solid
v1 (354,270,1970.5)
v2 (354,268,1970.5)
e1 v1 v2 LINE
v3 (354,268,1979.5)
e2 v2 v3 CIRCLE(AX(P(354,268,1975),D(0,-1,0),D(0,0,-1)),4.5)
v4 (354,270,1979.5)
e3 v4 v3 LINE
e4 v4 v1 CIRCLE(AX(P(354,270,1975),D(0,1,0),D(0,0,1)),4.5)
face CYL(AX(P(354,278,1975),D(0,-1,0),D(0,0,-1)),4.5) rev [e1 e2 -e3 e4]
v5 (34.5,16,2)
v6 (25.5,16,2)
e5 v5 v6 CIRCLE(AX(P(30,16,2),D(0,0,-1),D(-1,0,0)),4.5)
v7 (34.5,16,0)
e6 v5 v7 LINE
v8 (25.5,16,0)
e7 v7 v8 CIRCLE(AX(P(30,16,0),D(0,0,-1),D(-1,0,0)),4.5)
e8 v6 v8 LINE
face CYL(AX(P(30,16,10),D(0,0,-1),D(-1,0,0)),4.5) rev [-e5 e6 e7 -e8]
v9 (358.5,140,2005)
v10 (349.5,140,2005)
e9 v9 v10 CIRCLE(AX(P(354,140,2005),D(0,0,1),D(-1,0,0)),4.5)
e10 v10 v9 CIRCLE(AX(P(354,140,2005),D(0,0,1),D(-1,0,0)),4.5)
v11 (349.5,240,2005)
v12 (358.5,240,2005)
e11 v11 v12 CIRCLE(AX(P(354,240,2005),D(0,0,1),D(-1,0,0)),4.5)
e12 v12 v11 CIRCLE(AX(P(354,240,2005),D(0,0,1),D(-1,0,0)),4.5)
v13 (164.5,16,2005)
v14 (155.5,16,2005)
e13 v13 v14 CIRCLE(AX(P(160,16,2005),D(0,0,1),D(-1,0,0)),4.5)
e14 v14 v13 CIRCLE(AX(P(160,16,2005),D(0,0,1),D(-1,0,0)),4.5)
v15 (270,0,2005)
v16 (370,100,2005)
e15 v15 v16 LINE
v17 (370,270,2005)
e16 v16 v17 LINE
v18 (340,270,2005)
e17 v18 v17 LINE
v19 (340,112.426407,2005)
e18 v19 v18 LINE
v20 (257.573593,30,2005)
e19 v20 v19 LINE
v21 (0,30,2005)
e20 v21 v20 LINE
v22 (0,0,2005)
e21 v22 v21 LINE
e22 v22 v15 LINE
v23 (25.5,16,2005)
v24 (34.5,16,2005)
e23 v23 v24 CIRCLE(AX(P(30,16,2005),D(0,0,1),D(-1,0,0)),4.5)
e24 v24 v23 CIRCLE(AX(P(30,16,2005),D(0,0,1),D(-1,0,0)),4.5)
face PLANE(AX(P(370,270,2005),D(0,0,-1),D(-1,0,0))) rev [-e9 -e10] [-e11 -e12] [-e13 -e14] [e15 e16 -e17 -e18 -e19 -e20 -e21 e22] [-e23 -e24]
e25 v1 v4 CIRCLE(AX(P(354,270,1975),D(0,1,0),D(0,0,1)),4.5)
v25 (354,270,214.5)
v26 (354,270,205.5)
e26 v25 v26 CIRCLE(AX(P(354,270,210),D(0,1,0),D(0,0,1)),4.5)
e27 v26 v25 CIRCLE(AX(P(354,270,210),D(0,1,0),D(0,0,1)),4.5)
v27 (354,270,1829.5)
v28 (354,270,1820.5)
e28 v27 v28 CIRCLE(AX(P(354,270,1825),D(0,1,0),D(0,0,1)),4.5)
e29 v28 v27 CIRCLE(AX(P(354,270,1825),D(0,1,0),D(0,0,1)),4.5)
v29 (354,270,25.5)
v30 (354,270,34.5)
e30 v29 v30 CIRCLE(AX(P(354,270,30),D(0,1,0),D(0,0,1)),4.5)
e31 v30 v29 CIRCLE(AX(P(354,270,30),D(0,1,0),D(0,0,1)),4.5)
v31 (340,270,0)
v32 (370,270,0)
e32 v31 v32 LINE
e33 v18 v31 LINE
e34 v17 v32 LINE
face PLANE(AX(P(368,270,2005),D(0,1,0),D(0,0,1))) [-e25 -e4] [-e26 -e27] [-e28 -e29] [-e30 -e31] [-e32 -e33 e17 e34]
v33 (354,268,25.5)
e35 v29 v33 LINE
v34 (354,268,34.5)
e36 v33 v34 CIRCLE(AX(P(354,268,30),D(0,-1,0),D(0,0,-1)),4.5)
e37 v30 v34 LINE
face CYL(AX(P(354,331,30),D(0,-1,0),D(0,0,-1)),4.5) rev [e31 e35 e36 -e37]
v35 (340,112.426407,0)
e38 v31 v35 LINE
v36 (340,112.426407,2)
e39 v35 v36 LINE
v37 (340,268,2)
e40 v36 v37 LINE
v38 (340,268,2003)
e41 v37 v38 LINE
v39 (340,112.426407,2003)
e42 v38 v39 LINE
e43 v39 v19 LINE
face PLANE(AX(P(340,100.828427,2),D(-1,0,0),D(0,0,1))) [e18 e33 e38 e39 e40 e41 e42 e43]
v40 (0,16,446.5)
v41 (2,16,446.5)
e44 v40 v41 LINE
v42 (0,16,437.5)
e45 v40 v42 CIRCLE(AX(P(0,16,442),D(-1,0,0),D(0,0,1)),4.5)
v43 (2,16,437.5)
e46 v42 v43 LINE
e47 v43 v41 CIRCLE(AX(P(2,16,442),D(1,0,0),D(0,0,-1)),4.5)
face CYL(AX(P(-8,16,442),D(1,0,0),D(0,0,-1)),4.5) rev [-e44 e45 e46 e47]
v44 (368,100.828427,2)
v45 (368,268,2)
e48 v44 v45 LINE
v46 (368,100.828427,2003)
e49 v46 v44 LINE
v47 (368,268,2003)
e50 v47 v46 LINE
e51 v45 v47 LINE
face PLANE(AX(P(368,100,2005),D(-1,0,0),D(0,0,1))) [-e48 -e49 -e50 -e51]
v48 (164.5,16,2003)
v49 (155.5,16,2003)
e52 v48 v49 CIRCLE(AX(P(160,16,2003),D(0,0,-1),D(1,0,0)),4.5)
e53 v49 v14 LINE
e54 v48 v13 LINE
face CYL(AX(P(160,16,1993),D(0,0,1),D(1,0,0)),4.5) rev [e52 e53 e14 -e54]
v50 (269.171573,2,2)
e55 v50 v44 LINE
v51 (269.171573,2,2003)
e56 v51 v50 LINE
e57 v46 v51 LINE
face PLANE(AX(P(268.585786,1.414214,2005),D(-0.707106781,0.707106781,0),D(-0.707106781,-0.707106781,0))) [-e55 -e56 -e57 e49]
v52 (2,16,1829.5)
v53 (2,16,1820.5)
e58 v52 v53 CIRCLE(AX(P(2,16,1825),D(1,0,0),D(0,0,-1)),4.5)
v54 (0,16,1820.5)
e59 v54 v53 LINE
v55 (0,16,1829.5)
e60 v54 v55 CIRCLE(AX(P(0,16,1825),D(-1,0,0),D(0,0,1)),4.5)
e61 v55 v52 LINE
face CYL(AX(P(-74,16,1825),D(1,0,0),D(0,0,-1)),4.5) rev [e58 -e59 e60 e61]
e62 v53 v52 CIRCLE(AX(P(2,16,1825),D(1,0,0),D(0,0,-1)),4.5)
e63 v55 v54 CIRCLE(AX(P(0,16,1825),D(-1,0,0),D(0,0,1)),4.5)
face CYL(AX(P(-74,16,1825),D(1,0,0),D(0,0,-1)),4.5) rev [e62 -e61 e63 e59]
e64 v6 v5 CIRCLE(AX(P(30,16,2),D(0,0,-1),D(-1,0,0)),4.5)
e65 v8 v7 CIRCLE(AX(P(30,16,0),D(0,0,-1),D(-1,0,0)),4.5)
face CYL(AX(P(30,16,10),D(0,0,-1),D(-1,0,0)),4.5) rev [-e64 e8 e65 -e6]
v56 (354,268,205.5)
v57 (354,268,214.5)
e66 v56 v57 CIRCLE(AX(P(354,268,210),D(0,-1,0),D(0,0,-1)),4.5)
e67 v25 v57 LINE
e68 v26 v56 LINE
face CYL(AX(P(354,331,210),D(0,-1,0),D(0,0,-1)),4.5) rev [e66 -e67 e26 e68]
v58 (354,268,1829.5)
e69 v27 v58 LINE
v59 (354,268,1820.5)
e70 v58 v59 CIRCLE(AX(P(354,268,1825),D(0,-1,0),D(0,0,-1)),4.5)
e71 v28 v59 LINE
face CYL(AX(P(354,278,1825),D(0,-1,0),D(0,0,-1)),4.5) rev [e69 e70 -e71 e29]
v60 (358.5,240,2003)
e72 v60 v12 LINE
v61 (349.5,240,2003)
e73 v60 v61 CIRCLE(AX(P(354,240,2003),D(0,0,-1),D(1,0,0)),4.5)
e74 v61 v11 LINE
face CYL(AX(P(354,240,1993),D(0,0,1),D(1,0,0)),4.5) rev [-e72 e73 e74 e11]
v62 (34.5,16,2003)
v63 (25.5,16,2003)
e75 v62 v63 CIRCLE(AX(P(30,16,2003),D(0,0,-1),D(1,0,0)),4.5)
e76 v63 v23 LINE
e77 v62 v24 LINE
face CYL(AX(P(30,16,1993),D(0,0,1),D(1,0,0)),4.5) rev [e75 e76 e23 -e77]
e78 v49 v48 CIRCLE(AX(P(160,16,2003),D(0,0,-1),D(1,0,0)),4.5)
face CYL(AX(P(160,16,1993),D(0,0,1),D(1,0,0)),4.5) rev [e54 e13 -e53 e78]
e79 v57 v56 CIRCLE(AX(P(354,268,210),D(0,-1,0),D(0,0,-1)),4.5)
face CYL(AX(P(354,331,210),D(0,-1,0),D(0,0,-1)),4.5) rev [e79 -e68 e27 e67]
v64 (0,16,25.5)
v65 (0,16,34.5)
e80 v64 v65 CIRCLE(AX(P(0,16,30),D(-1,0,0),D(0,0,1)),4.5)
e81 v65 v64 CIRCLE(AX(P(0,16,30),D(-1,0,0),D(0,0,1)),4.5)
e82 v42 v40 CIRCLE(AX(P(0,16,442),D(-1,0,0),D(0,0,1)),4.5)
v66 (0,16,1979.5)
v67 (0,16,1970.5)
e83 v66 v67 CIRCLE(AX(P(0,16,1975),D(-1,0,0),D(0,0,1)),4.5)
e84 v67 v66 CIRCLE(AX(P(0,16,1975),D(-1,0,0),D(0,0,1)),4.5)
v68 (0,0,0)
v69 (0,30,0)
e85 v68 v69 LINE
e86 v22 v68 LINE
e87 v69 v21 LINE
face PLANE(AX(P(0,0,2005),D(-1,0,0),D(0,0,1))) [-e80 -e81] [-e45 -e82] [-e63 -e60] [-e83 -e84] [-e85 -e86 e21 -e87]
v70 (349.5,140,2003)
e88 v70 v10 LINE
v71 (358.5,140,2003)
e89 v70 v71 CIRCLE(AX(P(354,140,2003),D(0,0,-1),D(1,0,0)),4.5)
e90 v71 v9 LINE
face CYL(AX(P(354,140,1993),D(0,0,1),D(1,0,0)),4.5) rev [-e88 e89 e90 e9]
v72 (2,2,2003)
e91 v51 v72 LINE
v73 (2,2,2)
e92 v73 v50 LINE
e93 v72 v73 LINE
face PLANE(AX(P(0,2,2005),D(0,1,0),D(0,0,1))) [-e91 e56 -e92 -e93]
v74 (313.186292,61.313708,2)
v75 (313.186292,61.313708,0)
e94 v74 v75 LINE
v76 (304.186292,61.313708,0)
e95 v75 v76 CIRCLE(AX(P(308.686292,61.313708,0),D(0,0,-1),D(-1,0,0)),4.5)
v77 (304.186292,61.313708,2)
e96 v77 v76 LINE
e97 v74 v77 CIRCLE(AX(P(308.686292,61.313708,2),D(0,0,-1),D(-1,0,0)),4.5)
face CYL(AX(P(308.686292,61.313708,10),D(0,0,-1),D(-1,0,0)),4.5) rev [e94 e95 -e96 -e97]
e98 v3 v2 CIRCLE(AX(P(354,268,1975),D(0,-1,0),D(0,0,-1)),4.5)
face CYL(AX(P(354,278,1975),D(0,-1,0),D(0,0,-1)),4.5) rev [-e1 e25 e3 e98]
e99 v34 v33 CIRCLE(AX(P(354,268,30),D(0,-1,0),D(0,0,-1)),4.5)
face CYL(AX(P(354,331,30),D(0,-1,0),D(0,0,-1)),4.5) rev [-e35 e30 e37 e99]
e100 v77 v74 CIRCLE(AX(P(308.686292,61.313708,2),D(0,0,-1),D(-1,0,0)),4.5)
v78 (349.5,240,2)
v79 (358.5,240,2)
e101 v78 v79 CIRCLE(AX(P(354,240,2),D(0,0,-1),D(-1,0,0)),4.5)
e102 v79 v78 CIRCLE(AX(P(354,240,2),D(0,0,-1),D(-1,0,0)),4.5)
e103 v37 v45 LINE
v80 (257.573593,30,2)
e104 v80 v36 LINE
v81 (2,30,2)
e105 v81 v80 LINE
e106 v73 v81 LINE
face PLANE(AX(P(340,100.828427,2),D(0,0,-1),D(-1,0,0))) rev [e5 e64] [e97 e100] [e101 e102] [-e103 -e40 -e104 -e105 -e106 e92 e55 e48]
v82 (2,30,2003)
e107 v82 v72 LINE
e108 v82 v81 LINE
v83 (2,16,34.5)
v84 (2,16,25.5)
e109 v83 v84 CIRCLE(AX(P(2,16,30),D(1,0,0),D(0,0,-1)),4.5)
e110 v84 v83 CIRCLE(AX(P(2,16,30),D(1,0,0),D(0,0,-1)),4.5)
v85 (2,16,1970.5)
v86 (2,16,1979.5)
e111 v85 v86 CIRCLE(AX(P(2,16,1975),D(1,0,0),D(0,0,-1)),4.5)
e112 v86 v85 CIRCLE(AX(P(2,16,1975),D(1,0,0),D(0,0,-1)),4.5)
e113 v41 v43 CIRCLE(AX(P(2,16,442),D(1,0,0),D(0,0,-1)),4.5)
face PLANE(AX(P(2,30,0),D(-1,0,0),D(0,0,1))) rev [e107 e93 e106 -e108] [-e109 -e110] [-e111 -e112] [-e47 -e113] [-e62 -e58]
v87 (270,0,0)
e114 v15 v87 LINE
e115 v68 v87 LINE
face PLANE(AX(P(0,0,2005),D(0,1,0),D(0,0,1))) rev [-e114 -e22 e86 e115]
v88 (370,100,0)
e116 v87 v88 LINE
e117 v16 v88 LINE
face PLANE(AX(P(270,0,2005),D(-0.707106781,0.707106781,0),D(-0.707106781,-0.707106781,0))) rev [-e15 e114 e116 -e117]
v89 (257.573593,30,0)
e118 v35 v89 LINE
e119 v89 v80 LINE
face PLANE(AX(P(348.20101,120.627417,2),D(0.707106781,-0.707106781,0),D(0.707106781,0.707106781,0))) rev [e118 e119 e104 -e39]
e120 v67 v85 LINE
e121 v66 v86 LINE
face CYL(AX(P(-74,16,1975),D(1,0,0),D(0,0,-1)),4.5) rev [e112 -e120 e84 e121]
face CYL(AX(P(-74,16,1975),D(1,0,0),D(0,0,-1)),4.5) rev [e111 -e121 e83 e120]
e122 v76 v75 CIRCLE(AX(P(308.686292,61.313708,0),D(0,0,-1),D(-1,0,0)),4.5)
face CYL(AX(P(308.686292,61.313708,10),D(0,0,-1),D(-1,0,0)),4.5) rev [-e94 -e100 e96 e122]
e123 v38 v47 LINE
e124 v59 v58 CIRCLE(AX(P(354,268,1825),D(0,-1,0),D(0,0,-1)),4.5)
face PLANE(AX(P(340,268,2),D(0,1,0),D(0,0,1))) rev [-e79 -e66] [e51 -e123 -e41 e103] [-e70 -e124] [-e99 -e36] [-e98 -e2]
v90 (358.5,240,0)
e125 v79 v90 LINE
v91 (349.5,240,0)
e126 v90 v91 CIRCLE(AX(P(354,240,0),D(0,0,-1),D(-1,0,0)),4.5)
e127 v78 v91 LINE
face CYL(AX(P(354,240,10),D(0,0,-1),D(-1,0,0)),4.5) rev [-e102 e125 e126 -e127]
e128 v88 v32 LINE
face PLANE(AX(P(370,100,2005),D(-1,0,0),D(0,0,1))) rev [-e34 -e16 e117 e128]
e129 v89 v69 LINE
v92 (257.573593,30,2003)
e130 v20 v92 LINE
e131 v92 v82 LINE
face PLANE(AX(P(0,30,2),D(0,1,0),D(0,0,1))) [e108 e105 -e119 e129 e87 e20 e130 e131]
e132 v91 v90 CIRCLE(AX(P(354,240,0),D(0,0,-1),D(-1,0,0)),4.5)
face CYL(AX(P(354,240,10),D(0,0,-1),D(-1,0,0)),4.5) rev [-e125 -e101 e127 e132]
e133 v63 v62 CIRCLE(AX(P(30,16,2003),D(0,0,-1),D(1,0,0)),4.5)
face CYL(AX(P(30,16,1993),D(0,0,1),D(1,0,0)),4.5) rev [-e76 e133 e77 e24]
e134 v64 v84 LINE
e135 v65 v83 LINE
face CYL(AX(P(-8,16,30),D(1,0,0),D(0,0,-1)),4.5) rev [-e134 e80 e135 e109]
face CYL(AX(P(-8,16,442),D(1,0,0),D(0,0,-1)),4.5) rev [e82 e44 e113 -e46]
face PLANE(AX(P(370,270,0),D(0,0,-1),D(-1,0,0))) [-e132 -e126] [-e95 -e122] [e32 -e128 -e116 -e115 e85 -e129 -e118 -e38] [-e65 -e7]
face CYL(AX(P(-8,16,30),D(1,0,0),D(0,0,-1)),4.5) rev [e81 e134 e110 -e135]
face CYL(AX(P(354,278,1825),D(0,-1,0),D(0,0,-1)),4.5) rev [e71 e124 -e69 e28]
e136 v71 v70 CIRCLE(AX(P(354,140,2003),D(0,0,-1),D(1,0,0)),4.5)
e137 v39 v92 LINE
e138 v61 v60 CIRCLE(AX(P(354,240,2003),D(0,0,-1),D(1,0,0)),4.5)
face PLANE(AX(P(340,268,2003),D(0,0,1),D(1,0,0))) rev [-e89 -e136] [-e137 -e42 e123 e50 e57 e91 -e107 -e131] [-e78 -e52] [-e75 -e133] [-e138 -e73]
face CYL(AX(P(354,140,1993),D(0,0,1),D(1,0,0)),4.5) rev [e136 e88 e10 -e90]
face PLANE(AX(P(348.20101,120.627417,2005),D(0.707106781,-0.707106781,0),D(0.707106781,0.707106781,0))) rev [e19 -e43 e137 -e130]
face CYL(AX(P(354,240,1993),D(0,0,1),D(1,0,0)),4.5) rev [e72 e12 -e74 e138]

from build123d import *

# Parameters (mm, degrees)
EXTRUDE_1_DEPTH          = 2005
EXTRUDE_1_2_DEPTH        = 28
SKETCH_5_W               = 2
SKETCH_5_H               = 139.764501988
EXTRUDE_2_DEPTH          = 28
SKETCH_6_W               = 269.171572875
SKETCH_6_H               = 2
EXTRUDE_3_DEPTH          = 28
SKETCH_7_W               = 2
SKETCH_7_H               = 2005
EXTRUDE_4_DEPTH          = 28
CUT_EXTRUDE_1_DEPTH      = 10
CUT_EXTRUDE_1_DEPTH_BACK = 10
SKETCH_8_R               = 4.5
SKETCH_9_R               = 4.5
CUT_EXTRUDE_2_DEPTH      = 10
SKETCH_10_R              = 4.5
CUT_EXTRUDE_3_DEPTH      = 76
SKETCH_11_R              = 4.5
CUT_EXTRUDE_4_DEPTH      = 63
SKETCH_12_R              = 4.5
CUT_EXTRUDE_5_DEPTH      = 10
SKETCH_13_R              = 4.5
CUT_EXTRUDE_6_DEPTH      = 10


with BuildPart() as part:
    # 草图1 → Extrude 1 (new body)
    with BuildSketch(Plane.XY):
        Polygon((0, 0), (270, 0), (370, 100), (370, 270), (368, 270), (368, 100.828427125), (269.171572875, 2), (0, 2), align=None)
    extrude(amount=EXTRUDE_1_DEPTH)

    # 草图4 → Extrude 1 2 (add)
    with BuildSketch(Plane.ZY.offset(-368)):
        Polygon((0, 100.828427125), (0, 270), (2005, 270), (2005, 100.828427125), (2003, 100.828427125), (2003, 268), (2, 268), (2, 100.828427125), align=None)
    extrude(amount=EXTRUDE_1_2_DEPTH)

    # 草图5 → 凸台-拉伸2 (add)
    with BuildSketch(Plane(origin=(133.585786438, -133.585786438, 0), x_dir=(0, 0, 1), z_dir=(-0.7071067811865476, 0.7071067811865476, 0))):
        with Locations((1, 261.629509039)):
            Rectangle(SKETCH_5_W, SKETCH_5_H)
        with Locations((2004, 261.629509039)):
            Rectangle(SKETCH_5_W, SKETCH_5_H)
    extrude(amount=EXTRUDE_2_DEPTH)

    # 草图6 → 凸台-拉伸3 (add)
    with BuildSketch(Plane(origin=(0, 2, 0), x_dir=(1, 0, 0), z_dir=(0, 1, 0))):
        with Locations((134.585786438, -1)):
            Rectangle(SKETCH_6_W, SKETCH_6_H)
        with Locations((134.585786438, -2004)):
            Rectangle(SKETCH_6_W, SKETCH_6_H)
    extrude(amount=EXTRUDE_3_DEPTH)

    # 草图7 → 凸台-拉伸4 (add)
    with BuildSketch(Plane(origin=(0, 2, 0), x_dir=(1, 0, 0), z_dir=(0, 1, 0))):
        with Locations((1, -1002.5)):
            Rectangle(SKETCH_7_W, SKETCH_7_H)
    extrude(amount=EXTRUDE_4_DEPTH)

    # 草图8 → 切除-拉伸1 (cut, two sides: drawn at the far end of the back side and taken through both)
    with BuildSketch(Plane(origin=(0, 0, 2003), x_dir=(-1, 0, 0), z_dir=(0, 0, -1)).offset(-CUT_EXTRUDE_1_DEPTH_BACK)):
        with Locations(Location((-354, 240, 0), (0, 0, 180))):
            Circle(SKETCH_8_R)
        with Locations(Location((-30, 16, 0), (0, 0, 180))):
            Circle(SKETCH_8_R)
        with Locations(Location((-354, 140, 0), (0, 0, 180))):
            Circle(SKETCH_8_R)
        with Locations(Location((-160, 16, 0), (0, 0, 180))):
            Circle(SKETCH_8_R)
    extrude(amount=CUT_EXTRUDE_1_DEPTH + CUT_EXTRUDE_1_DEPTH_BACK, mode=Mode.SUBTRACT)

    # 草图9 → 切除-拉伸2 (cut)
    with BuildSketch(Plane.XZ.offset(-268)):
        with Locations(Location((354, 1975, 0), (0, 0, 270))):
            Circle(SKETCH_9_R)
        with Locations(Location((354, 1825, 0), (0, 0, 270))):
            Circle(SKETCH_9_R)
    extrude(amount=-CUT_EXTRUDE_2_DEPTH, mode=Mode.SUBTRACT)

    # 草图10 → 切除-拉伸3 (cut)
    with BuildSketch(Plane(origin=(2, 0, 0), x_dir=(0, 0, -1), z_dir=(1, 0, 0))):
        with Locations((-1975, 16)):
            Circle(SKETCH_10_R)
        with Locations((-1825, 16)):
            Circle(SKETCH_10_R)
    extrude(amount=-CUT_EXTRUDE_3_DEPTH, mode=Mode.SUBTRACT)

    # 草图11 → 切除-拉伸4 (cut)
    with BuildSketch(Plane.XZ.offset(-268)):
        with Locations(Location((354, 30, 0), (0, 0, 270))):
            Circle(SKETCH_11_R)
        with Locations(Location((354, 210, 0), (0, 0, 270))):
            Circle(SKETCH_11_R)
    extrude(amount=-CUT_EXTRUDE_4_DEPTH, mode=Mode.SUBTRACT)

    # 草图12 → 切除-拉伸5 (cut)
    with BuildSketch(Plane(origin=(2, 0, 0), x_dir=(0, 0, -1), z_dir=(1, 0, 0))):
        with Locations((-30, 16)):
            Circle(SKETCH_12_R)
        with Locations((-442, 16)):
            Circle(SKETCH_12_R)
    extrude(amount=-CUT_EXTRUDE_5_DEPTH, mode=Mode.SUBTRACT)

    # 草图13 → 切除-拉伸6 (cut)
    with BuildSketch(Plane(origin=(0, 0, 0), x_dir=(-1, 0, 0), z_dir=(0, 0, -1))):
        with Locations(Location((-30, 16, 0), (0, 0, 180))):
            Circle(SKETCH_13_R)
        with Locations(Location((-354, 240, 0), (0, 0, 180))):
            Circle(SKETCH_13_R)
        with Locations((-308.686291501, 61.313708499)):
            Circle(SKETCH_13_R)
    extrude(amount=-CUT_EXTRUDE_6_DEPTH, mode=Mode.SUBTRACT)


solid = part.part
